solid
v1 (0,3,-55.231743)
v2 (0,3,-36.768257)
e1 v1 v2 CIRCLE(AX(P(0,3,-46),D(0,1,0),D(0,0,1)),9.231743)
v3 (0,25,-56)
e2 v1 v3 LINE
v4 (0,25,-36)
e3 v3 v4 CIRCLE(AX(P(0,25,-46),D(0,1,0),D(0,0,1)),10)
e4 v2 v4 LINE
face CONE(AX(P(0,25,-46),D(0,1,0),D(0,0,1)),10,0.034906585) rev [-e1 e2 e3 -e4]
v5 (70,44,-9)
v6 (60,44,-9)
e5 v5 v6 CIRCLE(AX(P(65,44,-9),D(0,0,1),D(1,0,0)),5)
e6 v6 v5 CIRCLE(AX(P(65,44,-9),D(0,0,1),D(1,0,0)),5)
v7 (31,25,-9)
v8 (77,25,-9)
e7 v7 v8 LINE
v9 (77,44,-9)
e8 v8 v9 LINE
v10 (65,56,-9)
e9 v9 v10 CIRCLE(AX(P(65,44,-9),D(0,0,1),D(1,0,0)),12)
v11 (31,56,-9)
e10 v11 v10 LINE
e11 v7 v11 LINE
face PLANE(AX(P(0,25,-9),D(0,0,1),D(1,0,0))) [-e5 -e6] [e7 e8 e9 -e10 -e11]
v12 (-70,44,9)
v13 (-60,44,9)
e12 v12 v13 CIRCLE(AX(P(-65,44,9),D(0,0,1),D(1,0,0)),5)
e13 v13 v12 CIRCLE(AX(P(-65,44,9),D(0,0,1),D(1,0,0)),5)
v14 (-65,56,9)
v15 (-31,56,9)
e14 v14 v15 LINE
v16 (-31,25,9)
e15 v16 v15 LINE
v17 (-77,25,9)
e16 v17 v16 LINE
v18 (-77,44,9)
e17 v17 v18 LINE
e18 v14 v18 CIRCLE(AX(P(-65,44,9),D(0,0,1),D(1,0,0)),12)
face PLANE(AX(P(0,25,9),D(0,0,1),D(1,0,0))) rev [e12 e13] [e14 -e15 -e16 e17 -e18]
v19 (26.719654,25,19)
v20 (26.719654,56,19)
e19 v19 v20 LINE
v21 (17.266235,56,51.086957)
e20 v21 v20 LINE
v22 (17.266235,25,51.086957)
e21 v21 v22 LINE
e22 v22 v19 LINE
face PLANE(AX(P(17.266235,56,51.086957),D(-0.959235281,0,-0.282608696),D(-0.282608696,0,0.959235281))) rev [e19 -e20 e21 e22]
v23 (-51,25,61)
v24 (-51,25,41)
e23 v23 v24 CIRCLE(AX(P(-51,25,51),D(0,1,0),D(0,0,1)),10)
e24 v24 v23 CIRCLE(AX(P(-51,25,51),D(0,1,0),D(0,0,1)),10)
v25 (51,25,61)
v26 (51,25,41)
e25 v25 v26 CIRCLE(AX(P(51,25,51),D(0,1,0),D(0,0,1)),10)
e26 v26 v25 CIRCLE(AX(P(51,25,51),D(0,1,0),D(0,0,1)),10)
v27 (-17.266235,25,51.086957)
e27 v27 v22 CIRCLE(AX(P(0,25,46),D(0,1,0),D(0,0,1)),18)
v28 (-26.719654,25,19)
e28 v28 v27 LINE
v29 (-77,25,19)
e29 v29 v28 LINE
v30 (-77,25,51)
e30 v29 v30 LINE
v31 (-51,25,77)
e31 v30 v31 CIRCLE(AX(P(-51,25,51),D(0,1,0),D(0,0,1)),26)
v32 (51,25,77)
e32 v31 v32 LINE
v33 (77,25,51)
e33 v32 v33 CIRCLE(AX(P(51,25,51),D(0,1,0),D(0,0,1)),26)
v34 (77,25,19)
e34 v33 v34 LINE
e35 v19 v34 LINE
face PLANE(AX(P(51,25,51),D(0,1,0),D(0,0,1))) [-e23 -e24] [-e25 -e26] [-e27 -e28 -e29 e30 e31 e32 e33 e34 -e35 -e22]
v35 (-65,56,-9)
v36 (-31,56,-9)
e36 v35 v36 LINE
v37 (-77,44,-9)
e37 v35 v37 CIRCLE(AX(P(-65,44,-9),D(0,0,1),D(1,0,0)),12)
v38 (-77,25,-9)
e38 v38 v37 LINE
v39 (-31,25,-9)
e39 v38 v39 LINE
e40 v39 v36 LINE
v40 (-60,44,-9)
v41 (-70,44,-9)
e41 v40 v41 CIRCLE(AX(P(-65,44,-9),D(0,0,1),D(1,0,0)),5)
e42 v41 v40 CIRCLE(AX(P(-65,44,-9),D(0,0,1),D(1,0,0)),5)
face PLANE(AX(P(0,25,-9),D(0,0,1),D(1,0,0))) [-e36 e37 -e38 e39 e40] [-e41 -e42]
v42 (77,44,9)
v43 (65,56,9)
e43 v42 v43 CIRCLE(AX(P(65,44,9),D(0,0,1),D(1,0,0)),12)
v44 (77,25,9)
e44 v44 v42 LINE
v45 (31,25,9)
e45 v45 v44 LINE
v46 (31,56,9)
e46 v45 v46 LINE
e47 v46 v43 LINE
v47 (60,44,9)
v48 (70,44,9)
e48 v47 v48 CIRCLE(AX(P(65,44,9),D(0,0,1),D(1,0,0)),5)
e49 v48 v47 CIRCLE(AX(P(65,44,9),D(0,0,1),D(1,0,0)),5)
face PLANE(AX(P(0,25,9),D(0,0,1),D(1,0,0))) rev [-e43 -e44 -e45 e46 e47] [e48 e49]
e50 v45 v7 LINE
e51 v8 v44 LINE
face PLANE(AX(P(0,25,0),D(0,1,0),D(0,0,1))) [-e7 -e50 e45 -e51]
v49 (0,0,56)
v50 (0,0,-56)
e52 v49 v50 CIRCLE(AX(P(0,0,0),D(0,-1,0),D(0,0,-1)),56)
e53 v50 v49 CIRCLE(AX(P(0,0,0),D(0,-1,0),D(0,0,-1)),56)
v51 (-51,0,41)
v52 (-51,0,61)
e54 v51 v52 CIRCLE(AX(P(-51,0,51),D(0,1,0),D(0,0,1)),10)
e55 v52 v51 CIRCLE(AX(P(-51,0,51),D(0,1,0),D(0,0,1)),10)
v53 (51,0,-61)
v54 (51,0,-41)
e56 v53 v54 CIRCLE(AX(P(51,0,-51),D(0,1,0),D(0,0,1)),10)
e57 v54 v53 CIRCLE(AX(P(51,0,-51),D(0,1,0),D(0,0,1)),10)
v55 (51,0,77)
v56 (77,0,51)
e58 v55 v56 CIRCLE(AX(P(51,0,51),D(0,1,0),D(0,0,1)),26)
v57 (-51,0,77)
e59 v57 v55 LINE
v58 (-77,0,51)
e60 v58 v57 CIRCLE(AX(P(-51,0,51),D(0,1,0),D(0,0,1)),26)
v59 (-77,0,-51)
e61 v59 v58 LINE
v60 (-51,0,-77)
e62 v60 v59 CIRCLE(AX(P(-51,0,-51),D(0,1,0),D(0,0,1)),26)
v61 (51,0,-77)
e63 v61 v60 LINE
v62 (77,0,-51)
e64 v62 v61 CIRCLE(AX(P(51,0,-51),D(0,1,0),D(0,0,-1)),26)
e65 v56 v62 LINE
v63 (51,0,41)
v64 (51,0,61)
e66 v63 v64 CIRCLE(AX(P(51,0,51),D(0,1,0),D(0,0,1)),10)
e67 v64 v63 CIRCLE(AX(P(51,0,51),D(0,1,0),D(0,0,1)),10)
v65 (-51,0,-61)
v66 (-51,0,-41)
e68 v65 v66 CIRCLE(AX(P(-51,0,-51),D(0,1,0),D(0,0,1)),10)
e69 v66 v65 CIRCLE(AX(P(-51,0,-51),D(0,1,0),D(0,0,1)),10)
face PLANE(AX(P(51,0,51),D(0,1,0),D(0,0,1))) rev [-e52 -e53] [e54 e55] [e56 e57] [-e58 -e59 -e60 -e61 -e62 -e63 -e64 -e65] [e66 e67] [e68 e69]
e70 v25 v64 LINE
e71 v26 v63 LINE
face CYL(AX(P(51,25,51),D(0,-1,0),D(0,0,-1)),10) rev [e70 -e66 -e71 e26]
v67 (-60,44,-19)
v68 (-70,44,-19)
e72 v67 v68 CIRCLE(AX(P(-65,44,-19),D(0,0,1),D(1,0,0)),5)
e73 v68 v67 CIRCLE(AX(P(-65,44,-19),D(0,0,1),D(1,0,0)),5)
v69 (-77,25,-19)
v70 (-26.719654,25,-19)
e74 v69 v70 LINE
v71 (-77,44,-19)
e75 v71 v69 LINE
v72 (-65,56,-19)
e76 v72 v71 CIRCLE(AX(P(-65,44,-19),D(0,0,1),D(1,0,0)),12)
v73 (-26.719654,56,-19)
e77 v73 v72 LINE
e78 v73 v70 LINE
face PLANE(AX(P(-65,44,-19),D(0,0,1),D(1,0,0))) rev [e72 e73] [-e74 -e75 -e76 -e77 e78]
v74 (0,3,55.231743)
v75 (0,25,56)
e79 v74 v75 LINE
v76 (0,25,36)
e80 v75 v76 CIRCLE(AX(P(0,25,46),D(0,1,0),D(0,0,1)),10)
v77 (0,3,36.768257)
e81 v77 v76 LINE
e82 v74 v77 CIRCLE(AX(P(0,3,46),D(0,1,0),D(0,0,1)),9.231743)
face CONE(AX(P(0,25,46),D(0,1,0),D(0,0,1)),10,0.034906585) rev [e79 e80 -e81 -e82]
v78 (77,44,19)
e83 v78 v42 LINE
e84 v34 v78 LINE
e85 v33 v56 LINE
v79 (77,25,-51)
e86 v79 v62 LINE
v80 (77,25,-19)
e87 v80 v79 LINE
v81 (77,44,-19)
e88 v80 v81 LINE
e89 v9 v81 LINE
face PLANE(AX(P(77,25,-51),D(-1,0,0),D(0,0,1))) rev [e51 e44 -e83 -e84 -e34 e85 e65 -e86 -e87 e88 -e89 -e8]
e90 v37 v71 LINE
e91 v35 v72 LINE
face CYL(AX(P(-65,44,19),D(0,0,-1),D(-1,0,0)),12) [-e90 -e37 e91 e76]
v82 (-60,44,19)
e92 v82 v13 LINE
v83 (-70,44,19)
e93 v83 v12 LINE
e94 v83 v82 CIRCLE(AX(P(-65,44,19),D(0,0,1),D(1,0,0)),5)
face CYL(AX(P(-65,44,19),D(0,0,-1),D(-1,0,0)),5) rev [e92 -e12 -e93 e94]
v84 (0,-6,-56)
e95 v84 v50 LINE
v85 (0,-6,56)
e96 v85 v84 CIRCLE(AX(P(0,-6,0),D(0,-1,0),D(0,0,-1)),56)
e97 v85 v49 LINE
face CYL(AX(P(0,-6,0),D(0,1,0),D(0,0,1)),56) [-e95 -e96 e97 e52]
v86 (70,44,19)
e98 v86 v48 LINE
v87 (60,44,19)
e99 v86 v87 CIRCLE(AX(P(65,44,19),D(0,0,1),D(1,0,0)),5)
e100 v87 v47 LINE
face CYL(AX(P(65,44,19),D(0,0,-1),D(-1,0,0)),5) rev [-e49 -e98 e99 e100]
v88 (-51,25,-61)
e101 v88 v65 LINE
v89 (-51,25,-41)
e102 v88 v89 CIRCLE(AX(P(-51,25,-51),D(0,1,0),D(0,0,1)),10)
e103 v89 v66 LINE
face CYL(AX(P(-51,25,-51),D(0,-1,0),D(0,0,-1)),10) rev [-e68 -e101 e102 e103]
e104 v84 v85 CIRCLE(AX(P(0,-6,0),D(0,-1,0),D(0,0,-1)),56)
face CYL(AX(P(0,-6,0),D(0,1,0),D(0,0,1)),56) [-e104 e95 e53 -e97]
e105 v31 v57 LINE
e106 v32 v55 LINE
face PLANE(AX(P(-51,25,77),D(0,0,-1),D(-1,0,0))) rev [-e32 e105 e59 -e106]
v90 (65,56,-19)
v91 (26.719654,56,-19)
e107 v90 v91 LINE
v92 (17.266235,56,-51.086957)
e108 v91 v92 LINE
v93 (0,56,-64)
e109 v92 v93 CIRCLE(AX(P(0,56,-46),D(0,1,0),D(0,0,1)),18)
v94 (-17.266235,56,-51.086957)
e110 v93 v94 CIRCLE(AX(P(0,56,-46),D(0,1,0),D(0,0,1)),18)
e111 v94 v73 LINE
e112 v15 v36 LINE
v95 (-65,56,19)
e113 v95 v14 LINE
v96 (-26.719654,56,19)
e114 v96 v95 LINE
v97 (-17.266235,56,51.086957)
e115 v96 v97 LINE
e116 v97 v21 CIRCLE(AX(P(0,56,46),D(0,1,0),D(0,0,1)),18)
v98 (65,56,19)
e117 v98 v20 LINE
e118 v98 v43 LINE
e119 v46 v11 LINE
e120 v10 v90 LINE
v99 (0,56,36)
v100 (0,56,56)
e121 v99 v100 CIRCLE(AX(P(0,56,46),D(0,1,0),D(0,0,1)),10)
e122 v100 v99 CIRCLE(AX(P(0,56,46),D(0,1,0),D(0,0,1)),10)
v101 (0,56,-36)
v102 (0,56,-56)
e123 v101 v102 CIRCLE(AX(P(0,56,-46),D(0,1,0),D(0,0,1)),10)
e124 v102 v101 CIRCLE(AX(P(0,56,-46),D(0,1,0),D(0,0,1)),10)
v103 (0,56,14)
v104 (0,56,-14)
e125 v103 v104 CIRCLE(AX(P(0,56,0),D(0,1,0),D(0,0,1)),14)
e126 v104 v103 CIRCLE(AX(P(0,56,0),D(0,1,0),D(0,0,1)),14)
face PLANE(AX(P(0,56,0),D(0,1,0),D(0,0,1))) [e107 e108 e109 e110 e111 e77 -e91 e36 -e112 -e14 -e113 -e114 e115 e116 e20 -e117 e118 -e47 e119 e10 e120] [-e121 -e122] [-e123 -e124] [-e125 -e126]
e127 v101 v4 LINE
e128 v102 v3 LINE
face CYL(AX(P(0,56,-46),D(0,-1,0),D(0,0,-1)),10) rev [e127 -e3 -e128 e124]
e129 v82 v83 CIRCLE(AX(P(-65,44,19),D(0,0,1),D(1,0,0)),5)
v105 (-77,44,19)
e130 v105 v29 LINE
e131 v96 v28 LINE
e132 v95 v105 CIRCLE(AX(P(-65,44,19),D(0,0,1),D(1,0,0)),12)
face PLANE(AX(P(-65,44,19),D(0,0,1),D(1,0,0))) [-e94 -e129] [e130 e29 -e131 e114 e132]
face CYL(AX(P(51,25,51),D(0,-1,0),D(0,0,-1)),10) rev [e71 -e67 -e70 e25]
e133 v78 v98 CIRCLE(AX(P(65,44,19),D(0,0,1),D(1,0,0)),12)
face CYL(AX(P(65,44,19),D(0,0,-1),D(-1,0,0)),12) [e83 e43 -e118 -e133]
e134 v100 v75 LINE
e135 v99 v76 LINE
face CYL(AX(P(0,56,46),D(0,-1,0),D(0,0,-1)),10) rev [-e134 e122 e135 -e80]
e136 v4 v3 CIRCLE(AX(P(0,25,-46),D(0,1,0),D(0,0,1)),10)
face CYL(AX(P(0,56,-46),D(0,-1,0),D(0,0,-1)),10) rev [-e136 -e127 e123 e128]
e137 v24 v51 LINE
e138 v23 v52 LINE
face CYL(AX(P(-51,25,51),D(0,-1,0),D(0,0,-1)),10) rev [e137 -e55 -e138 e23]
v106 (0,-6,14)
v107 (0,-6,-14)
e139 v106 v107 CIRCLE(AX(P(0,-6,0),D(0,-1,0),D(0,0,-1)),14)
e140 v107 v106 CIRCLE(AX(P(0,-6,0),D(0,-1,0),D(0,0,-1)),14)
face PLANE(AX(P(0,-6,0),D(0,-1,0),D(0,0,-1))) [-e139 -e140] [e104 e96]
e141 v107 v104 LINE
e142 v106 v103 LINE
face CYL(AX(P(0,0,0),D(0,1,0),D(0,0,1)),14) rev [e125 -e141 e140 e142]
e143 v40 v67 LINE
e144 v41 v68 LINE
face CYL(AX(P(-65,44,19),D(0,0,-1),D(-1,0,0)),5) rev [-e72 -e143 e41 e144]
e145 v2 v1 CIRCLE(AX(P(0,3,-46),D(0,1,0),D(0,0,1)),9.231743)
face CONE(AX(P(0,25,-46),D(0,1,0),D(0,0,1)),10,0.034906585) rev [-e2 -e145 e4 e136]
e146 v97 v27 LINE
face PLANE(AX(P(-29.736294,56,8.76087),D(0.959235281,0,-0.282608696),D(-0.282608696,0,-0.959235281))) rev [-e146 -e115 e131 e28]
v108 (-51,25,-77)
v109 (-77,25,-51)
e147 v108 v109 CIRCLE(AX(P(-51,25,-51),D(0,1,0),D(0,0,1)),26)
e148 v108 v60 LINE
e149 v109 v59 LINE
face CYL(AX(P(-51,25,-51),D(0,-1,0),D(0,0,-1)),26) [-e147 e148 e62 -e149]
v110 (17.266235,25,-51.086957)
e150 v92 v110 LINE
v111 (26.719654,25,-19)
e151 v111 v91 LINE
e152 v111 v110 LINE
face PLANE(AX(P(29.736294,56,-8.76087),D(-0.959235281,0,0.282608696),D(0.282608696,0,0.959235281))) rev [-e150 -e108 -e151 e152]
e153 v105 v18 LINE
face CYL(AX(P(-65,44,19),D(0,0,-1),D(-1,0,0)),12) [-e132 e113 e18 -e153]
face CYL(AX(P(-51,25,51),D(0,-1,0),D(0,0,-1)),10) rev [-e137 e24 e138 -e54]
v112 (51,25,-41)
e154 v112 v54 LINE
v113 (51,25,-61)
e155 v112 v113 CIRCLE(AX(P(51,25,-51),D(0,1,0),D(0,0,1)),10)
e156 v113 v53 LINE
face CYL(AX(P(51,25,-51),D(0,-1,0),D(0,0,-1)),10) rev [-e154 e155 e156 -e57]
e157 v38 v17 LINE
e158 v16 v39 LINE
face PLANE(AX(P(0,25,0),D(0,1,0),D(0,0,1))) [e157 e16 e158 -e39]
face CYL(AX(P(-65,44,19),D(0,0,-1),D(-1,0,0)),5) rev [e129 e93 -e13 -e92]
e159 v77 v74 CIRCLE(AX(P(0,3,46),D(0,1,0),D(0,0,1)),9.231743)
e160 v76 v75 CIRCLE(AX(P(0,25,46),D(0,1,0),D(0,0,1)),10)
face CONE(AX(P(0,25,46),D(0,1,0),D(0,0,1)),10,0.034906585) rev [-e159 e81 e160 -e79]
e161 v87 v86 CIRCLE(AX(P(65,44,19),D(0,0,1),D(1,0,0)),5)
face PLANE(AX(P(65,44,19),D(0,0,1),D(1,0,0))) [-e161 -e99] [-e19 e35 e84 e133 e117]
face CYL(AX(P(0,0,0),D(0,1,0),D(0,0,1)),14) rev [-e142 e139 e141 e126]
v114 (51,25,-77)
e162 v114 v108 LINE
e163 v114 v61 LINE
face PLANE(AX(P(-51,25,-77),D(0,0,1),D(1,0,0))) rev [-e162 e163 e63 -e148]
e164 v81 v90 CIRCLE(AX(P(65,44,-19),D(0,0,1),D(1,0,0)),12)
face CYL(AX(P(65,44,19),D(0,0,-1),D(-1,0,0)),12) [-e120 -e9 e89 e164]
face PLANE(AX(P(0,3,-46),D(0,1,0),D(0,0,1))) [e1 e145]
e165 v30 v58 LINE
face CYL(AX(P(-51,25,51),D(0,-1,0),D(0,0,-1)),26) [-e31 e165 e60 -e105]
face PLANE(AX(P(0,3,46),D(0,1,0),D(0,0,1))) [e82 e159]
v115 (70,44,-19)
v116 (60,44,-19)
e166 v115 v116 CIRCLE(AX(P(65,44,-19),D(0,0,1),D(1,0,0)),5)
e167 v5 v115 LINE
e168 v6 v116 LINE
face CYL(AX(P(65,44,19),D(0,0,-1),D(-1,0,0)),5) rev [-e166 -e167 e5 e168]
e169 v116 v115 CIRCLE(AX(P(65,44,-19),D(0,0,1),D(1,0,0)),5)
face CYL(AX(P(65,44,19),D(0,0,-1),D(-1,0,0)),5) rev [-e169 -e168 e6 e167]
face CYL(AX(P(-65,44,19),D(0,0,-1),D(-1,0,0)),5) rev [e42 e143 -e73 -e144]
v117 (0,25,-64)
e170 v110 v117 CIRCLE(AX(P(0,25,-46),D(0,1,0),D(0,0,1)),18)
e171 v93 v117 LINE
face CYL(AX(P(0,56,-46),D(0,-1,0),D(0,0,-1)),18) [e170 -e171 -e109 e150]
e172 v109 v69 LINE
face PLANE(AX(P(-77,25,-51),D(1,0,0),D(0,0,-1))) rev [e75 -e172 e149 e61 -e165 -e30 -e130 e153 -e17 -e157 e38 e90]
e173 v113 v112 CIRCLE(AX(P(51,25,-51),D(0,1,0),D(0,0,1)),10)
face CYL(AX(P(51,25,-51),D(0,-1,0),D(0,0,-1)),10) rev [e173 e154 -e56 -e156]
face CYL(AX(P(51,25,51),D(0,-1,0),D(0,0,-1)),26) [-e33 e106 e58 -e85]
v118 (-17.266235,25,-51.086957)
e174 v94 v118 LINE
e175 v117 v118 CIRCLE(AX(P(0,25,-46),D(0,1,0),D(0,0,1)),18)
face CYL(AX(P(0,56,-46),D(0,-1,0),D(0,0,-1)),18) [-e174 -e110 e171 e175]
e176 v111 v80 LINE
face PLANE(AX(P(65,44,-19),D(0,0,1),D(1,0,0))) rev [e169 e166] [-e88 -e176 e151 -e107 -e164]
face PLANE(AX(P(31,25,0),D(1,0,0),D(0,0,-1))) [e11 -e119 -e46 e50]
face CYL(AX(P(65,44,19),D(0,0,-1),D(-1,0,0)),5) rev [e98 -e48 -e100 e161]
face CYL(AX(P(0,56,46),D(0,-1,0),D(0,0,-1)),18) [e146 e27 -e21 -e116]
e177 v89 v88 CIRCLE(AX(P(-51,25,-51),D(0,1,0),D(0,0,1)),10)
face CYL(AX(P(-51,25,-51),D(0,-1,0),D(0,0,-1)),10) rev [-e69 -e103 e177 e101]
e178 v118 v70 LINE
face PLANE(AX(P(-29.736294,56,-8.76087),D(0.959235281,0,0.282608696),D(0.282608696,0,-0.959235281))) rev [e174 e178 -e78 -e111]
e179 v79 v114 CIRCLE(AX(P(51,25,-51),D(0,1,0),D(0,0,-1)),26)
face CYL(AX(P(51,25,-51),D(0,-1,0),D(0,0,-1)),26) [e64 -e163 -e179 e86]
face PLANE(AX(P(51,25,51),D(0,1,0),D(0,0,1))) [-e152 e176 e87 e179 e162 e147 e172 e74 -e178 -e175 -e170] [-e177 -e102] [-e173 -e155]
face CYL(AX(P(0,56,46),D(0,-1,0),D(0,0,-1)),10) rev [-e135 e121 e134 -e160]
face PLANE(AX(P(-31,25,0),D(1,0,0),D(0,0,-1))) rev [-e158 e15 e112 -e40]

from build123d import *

# Parameters (mm, degrees)
BASE_PLATE_SKETCH_R                  = 10
BASE_PLATE_154X154_DEPTH             = 25
CENTRE_BORE_SKETCH_R                 = 14
CENTRE_BORE_28_DEPTH                 = 25
LOWER_RING_BOSS_SKETCH_R             = 56
LOWER_RING_BOSS_SKETCH_R_2           = 14
LOWER_RING_BOSS_112_DEPTH            = 6
CENTRAL_START                        = 31
CENTRAL_BOSS_SKETCH_R                = 20
CENTRAL_BOSS_SKETCH_R_2              = 14
CENTRAL_BOSS_40_DEPTH                = 31
CROSS_START                          = 31
CROSS_ARMS_SKETCH_R                  = 10
CROSS_ARMS_SKETCH_R_2                = 20
CROSS_ARMS_DEPTH                     = 31
ARM_SLOT_SKETCH_R                    = 10
ARM_SLOT_CUT_DRAFTED_DEPTH           = 22
ARM_SLOT_CUT_DRAFTED_DRAFT           = -2
ARM_SLOT_CUT_DRAFTED_PROFILE_2_DEPTH = 22
ARM_SLOT_CUT_DRAFTED_PROFILE_2_DRAFT = -2
CLEVIS_LUGS_SKETCH_R                 = 5
CLEVIS_LUGS_DEPTH                    = 19
ARM_POCKETS_SKETCH_W                 = 12
ARM_POCKETS_SKETCH_H                 = 18
ARM_POCKETS_AND_HOLES_DEPTH          = 31


with BuildPart() as part:
    # Base Plate Sketch → Base Plate 154x154 (new body)
    with BuildSketch(Plane(origin=(0, 0, 0), x_dir=(1, 0, 0), z_dir=(0, 1, 0))):
        with BuildLine():
            Line((-51, 77), (51, 77))
            ThreePointArc((51, 77), (69.384776311, 69.384776311), (77, 51))
            Line((77, 51), (77, -51))
            ThreePointArc((77, -51), (69.384776311, -69.384776311), (51, -77))
            Line((51, -77), (-51, -77))
            ThreePointArc((-51, -77), (-69.384776311, -69.384776311), (-77, -51))
            Line((-77, -51), (-77, 51))
            ThreePointArc((-77, 51), (-69.384776311, 69.384776311), (-51, 77))
        make_face()
        with Locations(Location((-51, 51, 0), (0, 0, 270))):
            Circle(BASE_PLATE_SKETCH_R, mode=Mode.SUBTRACT)
        with Locations(Location((51, 51, 0), (0, 0, 270))):
            Circle(BASE_PLATE_SKETCH_R, mode=Mode.SUBTRACT)
        with Locations(Location((51, -51, 0), (0, 0, 270))):
            Circle(BASE_PLATE_SKETCH_R, mode=Mode.SUBTRACT)
        with Locations(Location((-51, -51, 0), (0, 0, 270))):
            Circle(BASE_PLATE_SKETCH_R, mode=Mode.SUBTRACT)
    extrude(amount=BASE_PLATE_154X154_DEPTH)

    # Centre Bore Sketch → Centre Bore Ø28 (cut)
    with BuildSketch(Plane(origin=(0, 25, 0), x_dir=(1, 0, 0), z_dir=(0, 1, 0))):
        with Locations(Location((0, 0, 0), (0, 0, 270))):
            Circle(CENTRE_BORE_SKETCH_R)
    extrude(amount=-CENTRE_BORE_28_DEPTH, mode=Mode.SUBTRACT)

    # Lower Ring Boss Sketch → Lower Ring Boss Ø112 (add)
    with BuildSketch(Plane.XZ):
        with Locations(Location((0, 0, 0), (0, 0, 270))):
            Circle(LOWER_RING_BOSS_SKETCH_R)
        with Locations(Location((0, 0, 0), (0, 0, 90))):
            Circle(LOWER_RING_BOSS_SKETCH_R_2, mode=Mode.SUBTRACT)
    extrude(amount=LOWER_RING_BOSS_112_DEPTH)

    # Central Boss Sketch → Central Boss Ø40 (add)
    with BuildSketch(Plane(origin=(0, 25, 0), x_dir=(1, 0, 0), z_dir=(0, 1, 0)).offset(CENTRAL_START)):
        with Locations(Location((0, 0, 0), (0, 0, 270))):
            Circle(CENTRAL_BOSS_SKETCH_R)
        with Locations(Location((0, 0, 0), (0, 0, 270))):
            Circle(CENTRAL_BOSS_SKETCH_R_2, mode=Mode.SUBTRACT)
    extrude(amount=-CENTRAL_BOSS_40_DEPTH)

    # Cross Arms Sketch → Cross Arms (add)
    with BuildSketch(Plane(origin=(0, 25, 0), x_dir=(1, 0, 0), z_dir=(0, 1, 0)).offset(CROSS_START)):
        with BuildLine():
            Line((-29.736293724, 8.760869565), (-17.266235066, 51.086956522))
            ThreePointArc((-17.266235066, 51.086956522), (0, 64), (17.266235066, 51.086956522))
            Line((17.266235066, 51.086956522), (29.736293724, 8.760869565))
            ThreePointArc((29.736293724, 8.760869565), (31, 0), (29.736293724, -8.760869565))
            Line((29.736293724, -8.760869565), (17.266235066, -51.086956522))
            ThreePointArc((17.266235066, -51.086956522), (0, -64), (-17.266235066, -51.086956522))
            Line((-17.266235066, -51.086956522), (-29.736293724, -8.760869565))
            ThreePointArc((-29.736293724, -8.760869565), (-31, 0), (-29.736293724, 8.760869565))
        make_face()
        with Locations(Location((0, 46, 0), (0, 0, 270))):
            Circle(CROSS_ARMS_SKETCH_R, mode=Mode.SUBTRACT)
        with Locations(Location((0, -46, 0), (0, 0, 270))):
            Circle(CROSS_ARMS_SKETCH_R, mode=Mode.SUBTRACT)
        Circle(CROSS_ARMS_SKETCH_R_2, mode=Mode.SUBTRACT)
    extrude(amount=-CROSS_ARMS_DEPTH)


with BuildPart() as arm_slot_cut_drafted_tool:
    # Arm Slot Sketch → Arm Slot Cut Drafted (with draft: the straight prism first)
    with BuildSketch(Plane(origin=(0, 25, 0), x_dir=(1, 0, 0), z_dir=(0, 1, 0))):
        with Locations(Location((0, 46, 0), (0, 0, 270))):
            Circle(ARM_SLOT_SKETCH_R)
    extrude(amount=-ARM_SLOT_CUT_DRAFTED_DEPTH)
    # Arm Slot Cut Drafted: the draft: its side faces are tilted about the plane it starts from
    arm_slot_cut_drafted_sides = [arm_slot_cut_drafted_tool.faces().sort_by_distance(p)[0] for p in [
        (0, 14, -56),
    ]]
    draft(arm_slot_cut_drafted_sides, Plane(origin=(0, 25, 0), x_dir=(1, 0, 0), z_dir=(0, 1, 0)), ARM_SLOT_CUT_DRAFTED_DRAFT)


with BuildPart() as part_1:
    add(part.part)

    # Arm Slot Cut Drafted: cut by arm_slot_cut_drafted_tool
    add(arm_slot_cut_drafted_tool.part, mode=Mode.SUBTRACT)


with BuildPart() as arm_slot_cut_drafted_profile_2_tool:
    # Arm Slot Sketch → Arm Slot Cut Drafted profile 2 (with draft: the straight prism first)
    with BuildSketch(Plane(origin=(0, 25, 0), x_dir=(1, 0, 0), z_dir=(0, 1, 0))):
        with Locations(Location((0, -46, 0), (0, 0, 270))):
            Circle(ARM_SLOT_SKETCH_R)
    extrude(amount=-ARM_SLOT_CUT_DRAFTED_PROFILE_2_DEPTH)
    # Arm Slot Cut Drafted profile 2: the draft: its side faces are tilted about the plane it starts from
    arm_slot_cut_drafted_profile_2_sides = [arm_slot_cut_drafted_profile_2_tool.faces().sort_by_distance(p)[0] for p in [
        (0, 14, 36),
    ]]
    draft(arm_slot_cut_drafted_profile_2_sides, Plane(origin=(0, 25, 0), x_dir=(1, 0, 0), z_dir=(0, 1, 0)), ARM_SLOT_CUT_DRAFTED_PROFILE_2_DRAFT)


with BuildPart() as part_2:
    add(part_1.part)

    # Arm Slot Cut Drafted profile 2: cut by arm_slot_cut_drafted_profile_2_tool
    add(arm_slot_cut_drafted_profile_2_tool.part, mode=Mode.SUBTRACT)

    # Clevis Lugs Sketch → Clevis Lugs (add, symmetric)
    # profile 1 of 2: a face of its own
    with BuildSketch(Plane.XY):
        with BuildLine():
            Line((-19.336072892, 56), (-65, 56))
            ThreePointArc((-65, 56), (-73.485281374, 52.485281374), (-77, 44))
            Line((-77, 44), (-77, 25))
            Line((-77, 25), (-19.336072892, 25))
            Line((-19.336072892, 25), (-19.336072892, 56))
        make_face()
        with Locations((-65, 44)):
            Circle(CLEVIS_LUGS_SKETCH_R, mode=Mode.SUBTRACT)
    # profile 2 of 2: a face of its own
    with BuildSketch(Plane.XY):
        with BuildLine():
            Line((77, 25), (77, 44))
            ThreePointArc((77, 44), (73.485281374, 52.485281374), (65, 56))
            Line((65, 56), (20.121294127, 56))
            Line((20.121294127, 56), (20.121294127, 25))
            Line((20.121294127, 25), (77, 25))
        make_face()
        with Locations((65, 44)):
            Circle(CLEVIS_LUGS_SKETCH_R, mode=Mode.SUBTRACT)
    extrude(amount=CLEVIS_LUGS_DEPTH, both=True)

    # Arm Pockets Sketch → Arm Pockets and Holes (cut)
    with BuildSketch(Plane(origin=(0, 56, 0), x_dir=(1, 0, 0), z_dir=(0, 1, 0))):
        Polygon((-31, 9), (-65, 9), (-65, -9), (-31, -9), (-31, 0), align=None)
        with Locations((-71, 0)):
            Rectangle(ARM_POCKETS_SKETCH_W, ARM_POCKETS_SKETCH_H)
        Polygon((31, 9), (31, 0), (31, -9), (65, -9), (65, 9), align=None)
        with Locations((71, 0)):
            Rectangle(ARM_POCKETS_SKETCH_W, ARM_POCKETS_SKETCH_H)
    extrude(amount=-ARM_POCKETS_AND_HOLES_DEPTH, mode=Mode.SUBTRACT)


solid = part_2.part
